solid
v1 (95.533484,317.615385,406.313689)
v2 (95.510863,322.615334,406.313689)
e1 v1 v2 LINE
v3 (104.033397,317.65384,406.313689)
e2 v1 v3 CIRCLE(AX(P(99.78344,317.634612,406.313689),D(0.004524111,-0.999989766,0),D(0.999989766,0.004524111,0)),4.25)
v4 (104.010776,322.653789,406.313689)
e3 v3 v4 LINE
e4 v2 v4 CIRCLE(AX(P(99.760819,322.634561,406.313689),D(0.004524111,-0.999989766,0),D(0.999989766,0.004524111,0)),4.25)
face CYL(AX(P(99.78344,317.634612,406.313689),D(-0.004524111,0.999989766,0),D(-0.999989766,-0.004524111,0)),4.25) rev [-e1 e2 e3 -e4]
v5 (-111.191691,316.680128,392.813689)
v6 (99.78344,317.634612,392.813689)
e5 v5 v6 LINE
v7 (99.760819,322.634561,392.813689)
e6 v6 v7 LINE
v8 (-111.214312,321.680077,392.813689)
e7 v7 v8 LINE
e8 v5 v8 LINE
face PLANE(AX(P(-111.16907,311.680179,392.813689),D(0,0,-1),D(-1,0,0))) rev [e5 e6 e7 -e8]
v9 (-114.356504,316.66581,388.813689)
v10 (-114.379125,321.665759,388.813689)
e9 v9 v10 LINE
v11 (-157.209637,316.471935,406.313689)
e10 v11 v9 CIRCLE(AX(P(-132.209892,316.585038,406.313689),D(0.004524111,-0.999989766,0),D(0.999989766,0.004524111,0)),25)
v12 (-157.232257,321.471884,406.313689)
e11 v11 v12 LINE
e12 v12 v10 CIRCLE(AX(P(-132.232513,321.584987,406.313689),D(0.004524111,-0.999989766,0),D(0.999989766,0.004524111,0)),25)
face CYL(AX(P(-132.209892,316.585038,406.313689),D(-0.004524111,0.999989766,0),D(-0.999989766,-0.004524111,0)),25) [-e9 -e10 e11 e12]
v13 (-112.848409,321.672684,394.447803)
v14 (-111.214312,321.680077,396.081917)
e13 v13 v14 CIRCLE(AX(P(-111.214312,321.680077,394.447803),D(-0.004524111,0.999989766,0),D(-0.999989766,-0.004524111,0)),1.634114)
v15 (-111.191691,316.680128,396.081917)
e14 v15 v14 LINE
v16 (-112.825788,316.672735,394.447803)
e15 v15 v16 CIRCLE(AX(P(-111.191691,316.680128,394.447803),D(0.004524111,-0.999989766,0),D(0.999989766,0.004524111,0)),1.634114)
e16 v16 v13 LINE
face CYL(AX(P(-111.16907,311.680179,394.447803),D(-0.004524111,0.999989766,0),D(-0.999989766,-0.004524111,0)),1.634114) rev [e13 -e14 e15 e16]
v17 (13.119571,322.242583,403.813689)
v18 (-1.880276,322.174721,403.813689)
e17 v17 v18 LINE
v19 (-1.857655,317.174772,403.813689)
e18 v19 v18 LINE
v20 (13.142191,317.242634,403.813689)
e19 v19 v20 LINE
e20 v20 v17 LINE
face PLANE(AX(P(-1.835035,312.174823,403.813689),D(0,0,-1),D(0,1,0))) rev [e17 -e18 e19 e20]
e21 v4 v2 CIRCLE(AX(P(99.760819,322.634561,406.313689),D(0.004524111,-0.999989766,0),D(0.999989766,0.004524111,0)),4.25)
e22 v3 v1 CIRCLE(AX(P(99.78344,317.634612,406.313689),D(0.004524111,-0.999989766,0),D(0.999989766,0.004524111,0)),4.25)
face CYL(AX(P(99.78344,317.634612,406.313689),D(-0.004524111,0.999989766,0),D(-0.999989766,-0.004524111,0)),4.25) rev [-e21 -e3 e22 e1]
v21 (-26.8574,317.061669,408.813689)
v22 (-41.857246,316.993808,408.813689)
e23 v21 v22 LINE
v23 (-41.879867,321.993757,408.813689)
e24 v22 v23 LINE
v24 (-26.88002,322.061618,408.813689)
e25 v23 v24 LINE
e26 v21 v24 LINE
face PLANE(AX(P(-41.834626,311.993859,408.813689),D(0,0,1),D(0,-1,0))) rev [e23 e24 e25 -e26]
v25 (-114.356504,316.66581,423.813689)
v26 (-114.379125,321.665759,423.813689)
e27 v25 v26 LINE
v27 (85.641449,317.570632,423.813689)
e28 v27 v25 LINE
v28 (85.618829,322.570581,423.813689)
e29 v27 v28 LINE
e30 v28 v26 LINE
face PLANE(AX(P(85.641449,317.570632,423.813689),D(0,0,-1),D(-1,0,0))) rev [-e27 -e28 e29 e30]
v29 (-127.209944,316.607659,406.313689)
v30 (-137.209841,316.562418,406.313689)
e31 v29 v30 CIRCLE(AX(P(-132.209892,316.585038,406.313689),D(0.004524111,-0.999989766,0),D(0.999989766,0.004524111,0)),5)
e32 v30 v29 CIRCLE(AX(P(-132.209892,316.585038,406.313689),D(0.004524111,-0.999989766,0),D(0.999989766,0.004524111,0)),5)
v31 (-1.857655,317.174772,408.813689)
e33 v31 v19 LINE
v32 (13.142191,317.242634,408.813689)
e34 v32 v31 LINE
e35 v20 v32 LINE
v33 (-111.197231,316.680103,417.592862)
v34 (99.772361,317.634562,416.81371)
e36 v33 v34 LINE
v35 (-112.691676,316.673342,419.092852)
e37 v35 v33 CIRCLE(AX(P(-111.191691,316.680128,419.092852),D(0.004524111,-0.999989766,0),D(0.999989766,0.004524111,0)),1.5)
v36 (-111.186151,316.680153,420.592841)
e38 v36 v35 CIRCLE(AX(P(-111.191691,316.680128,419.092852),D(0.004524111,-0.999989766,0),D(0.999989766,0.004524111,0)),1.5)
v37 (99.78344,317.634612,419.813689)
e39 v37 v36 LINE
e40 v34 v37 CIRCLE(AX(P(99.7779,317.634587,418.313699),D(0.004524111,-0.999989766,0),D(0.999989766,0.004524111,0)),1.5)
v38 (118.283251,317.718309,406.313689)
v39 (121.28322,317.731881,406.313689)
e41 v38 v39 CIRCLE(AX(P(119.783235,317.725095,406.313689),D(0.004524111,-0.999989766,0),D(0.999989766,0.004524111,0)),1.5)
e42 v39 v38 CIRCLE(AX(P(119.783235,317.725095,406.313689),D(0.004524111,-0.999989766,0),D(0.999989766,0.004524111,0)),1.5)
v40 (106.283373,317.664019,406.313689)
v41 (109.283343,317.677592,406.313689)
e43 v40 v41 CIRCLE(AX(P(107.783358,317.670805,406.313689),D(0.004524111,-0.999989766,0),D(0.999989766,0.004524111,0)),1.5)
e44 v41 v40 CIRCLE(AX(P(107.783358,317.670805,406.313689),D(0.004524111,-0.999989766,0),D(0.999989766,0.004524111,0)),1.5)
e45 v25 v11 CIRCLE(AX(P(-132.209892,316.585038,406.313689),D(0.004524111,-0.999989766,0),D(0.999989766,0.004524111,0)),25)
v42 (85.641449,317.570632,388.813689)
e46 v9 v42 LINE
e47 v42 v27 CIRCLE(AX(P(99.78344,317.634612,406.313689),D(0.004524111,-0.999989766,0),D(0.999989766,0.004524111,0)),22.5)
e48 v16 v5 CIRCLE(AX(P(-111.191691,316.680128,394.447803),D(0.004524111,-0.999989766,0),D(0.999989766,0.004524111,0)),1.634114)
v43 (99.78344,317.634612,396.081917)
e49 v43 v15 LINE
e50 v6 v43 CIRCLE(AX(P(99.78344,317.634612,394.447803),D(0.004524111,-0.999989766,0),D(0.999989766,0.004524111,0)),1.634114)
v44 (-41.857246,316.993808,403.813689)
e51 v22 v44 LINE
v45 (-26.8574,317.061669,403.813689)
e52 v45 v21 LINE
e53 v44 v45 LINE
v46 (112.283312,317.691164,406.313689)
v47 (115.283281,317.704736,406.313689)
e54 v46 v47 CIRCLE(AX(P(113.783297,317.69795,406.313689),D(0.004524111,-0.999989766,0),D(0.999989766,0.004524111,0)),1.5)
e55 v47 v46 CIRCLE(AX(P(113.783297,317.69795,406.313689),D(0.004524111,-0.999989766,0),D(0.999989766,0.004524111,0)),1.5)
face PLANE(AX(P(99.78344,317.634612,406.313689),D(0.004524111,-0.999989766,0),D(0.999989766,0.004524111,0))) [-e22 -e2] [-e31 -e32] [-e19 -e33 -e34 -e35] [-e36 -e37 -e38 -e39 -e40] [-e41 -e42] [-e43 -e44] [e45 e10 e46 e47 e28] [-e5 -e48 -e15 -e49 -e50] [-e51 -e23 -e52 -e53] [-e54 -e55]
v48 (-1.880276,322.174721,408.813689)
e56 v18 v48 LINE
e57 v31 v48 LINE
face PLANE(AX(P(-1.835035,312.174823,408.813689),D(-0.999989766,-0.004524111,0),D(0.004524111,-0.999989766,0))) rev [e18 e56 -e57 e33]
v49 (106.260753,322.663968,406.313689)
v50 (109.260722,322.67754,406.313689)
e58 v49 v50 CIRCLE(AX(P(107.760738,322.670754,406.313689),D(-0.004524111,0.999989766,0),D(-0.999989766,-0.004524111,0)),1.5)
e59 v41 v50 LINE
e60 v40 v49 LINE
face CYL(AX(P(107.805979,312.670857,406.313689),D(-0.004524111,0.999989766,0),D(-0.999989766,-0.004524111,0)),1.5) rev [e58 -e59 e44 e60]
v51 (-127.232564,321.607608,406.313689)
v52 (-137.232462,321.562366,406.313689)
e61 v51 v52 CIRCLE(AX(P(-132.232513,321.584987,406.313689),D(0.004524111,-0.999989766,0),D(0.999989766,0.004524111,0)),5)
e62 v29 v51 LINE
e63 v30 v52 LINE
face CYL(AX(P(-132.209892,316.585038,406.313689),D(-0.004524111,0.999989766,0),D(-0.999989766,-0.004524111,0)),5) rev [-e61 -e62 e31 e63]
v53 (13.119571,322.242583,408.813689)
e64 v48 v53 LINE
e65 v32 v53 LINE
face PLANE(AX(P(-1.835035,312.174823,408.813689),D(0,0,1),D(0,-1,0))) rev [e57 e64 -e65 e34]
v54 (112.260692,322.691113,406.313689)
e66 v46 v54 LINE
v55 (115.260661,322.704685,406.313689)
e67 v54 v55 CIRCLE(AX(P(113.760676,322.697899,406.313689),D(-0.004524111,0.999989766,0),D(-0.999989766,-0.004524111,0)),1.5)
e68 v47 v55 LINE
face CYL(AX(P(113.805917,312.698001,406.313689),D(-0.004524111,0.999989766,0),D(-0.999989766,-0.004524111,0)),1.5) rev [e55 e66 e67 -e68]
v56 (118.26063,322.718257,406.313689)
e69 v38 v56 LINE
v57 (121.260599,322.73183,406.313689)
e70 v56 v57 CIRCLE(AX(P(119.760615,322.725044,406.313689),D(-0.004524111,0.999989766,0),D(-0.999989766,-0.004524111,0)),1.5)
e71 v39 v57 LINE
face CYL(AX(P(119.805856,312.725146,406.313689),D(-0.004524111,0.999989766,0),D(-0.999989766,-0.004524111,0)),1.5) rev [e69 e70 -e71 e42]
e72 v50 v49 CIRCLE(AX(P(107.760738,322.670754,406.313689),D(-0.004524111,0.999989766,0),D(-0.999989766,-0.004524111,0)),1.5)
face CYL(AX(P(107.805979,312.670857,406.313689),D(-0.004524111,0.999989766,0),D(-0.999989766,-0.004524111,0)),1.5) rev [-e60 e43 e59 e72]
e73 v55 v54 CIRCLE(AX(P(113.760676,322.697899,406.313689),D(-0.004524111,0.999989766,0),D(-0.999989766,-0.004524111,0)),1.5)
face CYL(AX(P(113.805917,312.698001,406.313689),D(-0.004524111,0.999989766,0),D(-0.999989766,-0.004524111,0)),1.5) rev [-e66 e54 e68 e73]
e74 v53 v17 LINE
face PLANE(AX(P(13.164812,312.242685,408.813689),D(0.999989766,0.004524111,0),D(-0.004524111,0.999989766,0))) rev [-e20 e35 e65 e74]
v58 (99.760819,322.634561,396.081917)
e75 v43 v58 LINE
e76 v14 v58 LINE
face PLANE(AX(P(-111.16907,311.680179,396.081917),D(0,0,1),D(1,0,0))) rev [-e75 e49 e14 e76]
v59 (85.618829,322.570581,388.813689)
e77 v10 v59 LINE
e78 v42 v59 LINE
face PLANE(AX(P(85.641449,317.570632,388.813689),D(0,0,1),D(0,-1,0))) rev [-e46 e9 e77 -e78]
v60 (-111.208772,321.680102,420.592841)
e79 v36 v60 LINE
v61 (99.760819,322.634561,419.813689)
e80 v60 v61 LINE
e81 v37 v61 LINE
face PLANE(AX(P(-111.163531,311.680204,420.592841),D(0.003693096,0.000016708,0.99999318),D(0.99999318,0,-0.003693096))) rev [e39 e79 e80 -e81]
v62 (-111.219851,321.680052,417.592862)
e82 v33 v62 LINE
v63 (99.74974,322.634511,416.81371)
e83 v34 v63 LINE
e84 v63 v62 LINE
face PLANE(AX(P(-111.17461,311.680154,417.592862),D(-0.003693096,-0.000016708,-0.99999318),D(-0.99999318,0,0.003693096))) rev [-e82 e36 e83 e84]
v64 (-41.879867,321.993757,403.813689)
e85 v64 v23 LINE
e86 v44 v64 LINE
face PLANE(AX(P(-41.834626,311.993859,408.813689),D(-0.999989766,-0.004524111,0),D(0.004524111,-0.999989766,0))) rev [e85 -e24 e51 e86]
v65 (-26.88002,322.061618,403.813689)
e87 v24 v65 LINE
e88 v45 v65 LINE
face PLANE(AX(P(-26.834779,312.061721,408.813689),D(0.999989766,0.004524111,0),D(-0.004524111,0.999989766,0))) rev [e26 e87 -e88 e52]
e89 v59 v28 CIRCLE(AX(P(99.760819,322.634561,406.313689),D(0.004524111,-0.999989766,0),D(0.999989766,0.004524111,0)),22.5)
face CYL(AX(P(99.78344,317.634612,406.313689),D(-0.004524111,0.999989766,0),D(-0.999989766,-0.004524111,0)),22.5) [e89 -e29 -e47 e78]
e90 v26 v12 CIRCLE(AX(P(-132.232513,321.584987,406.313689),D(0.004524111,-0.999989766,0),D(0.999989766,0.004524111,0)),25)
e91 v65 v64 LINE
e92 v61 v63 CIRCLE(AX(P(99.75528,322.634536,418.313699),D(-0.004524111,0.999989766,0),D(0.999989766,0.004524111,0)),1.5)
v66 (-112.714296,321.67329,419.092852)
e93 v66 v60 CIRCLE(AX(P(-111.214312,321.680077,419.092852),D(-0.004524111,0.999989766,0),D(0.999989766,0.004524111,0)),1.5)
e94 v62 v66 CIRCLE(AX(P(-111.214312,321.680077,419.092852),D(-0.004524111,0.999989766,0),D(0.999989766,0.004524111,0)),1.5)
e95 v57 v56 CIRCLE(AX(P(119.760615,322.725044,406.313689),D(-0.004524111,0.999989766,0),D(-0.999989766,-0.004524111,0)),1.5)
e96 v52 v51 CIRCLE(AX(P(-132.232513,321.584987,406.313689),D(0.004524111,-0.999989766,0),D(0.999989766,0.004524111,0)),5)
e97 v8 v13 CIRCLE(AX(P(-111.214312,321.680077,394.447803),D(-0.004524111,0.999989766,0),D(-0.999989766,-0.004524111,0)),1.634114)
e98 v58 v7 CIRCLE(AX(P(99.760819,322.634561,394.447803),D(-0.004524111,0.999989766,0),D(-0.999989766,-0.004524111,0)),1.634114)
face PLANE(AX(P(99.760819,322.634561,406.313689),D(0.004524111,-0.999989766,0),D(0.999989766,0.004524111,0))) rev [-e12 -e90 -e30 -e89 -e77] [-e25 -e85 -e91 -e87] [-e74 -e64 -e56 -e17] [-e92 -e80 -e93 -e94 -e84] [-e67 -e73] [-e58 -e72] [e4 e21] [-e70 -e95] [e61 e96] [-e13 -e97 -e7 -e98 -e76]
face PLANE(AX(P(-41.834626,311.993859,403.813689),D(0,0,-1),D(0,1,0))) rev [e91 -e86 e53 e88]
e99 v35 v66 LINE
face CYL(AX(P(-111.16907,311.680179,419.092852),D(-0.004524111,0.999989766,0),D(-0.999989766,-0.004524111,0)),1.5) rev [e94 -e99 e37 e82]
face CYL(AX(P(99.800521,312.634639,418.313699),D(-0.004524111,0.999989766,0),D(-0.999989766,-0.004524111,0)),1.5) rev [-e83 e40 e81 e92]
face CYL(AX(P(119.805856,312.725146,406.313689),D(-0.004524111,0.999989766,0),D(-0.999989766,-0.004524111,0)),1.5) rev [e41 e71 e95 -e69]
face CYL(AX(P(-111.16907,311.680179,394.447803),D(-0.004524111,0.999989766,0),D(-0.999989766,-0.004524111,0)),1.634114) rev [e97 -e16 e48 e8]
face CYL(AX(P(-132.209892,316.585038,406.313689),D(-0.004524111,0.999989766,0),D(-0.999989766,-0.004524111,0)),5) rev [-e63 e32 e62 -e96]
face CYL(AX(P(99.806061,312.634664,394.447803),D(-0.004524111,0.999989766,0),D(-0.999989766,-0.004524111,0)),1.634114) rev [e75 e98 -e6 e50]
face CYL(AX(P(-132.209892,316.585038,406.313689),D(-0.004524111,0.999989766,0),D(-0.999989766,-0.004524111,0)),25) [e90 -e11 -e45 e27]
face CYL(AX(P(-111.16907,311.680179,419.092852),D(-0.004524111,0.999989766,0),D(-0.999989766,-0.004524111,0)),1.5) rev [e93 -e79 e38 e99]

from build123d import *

# Parameters (mm, degrees)
SKETCH_1_R          = 4.25
SKETCH_1_R_2        = 5
EXTRUDE_1_DEPTH     = 5
SKETCH_2_R          = 4.25
SKETCH_2_R_2        = 1.5
CUT_EXTRUDE_1_DEPTH = 10
CUT_EXTRUDE_2_DEPTH = 10
SKETCH_4_W          = 15
SKETCH_4_H          = 5
CUT_EXTRUDE_3_DEPTH = 10


with BuildPart() as part:
    # 草图1 → 凸台-拉伸1 (new body)
    with BuildSketch(Plane(origin=(-1.457577728, 322.176633369, 0), x_dir=(0.9999897661580252, 0.004524110875991417, 0), z_dir=(0.004524110875991416, -0.999989766158025, 0))):
        with BuildLine():
            Line((87.077297431, 423.813689202), (-112.922702569, 423.813689202))
            ThreePointArc((-112.922702569, 423.813689202), (-155.776273641, 406.313689202), (-112.922702569, 388.813689202))
            Line((-112.922702569, 388.813689202), (87.077297431, 388.813689202))
            ThreePointArc((87.077297431, 388.813689202), (123.719433055, 406.313689202), (87.077297431, 423.813689202))
        make_face()
        with Locations((101.219433055, 406.313689202)):
            Circle(SKETCH_1_R, mode=Mode.SUBTRACT)
        with Locations((-130.776273641, 406.313689202)):
            Circle(SKETCH_1_R_2, mode=Mode.SUBTRACT)
    extrude(amount=EXTRUDE_1_DEPTH)

    # 草图2 → 切除-拉伸1 (cut)
    with BuildSketch(Plane(origin=(-1.457577728, 322.176633369, 0), x_dir=(0.9999897661580252, 0.004524110875991416, 0), z_dir=(-0.004524110875991415, 0.999989766158025, 0))):
        with Locations((101.219433055, -406.313689202)):
            Circle(SKETCH_2_R)
        with Locations(Location((121.219433055, -406.313689202, 0), (0, 0, 180))):
            Circle(SKETCH_2_R_2)
        with Locations(Location((115.219433055, -406.313689202, 0), (0, 0, 180))):
            Circle(SKETCH_2_R_2)
        with Locations(Location((109.219433055, -406.313689202, 0), (0, 0, 180))):
            Circle(SKETCH_2_R_2)
        with Locations((-41.214218621, -347.791207337)):
            Circle(SKETCH_2_R_2)
        with Locations((-45.456859308, -343.54856665)):
            Circle(SKETCH_2_R_2)
        with Locations((-49.699499995, -339.305925963)):
            Circle(SKETCH_2_R_2)
        with Locations((-114.690511434, -191.551626966)):
            Circle(SKETCH_2_R_2)
        with Locations((-114.690511434, -185.551626966)):
            Circle(SKETCH_2_R_2)
        with Locations((-114.690511434, -179.551626966)):
            Circle(SKETCH_2_R_2)
        with Locations((-56.168029569, -29.117975291)):
            Circle(SKETCH_2_R_2)
        with Locations((-51.925388882, -24.875334604)):
            Circle(SKETCH_2_R_2)
        with Locations((-47.682748195, -20.632693917)):
            Circle(SKETCH_2_R_2)
        with Locations((100.071550802, 44.358317523)):
            Circle(SKETCH_2_R_2)
        with Locations((106.071550802, 44.358317523)):
            Circle(SKETCH_2_R_2)
        with Locations((112.071550802, 44.358317523)):
            Circle(SKETCH_2_R_2)
        with Locations((262.505202477, -14.164164342)):
            Circle(SKETCH_2_R_2)
        with Locations((266.747843164, -18.406805029)):
            Circle(SKETCH_2_R_2)
        with Locations((270.990483851, -22.649445716)):
            Circle(SKETCH_2_R_2)
        with Locations((335.981495291, -170.403744713)):
            Circle(SKETCH_2_R_2)
        with Locations((335.981495291, -176.403744713)):
            Circle(SKETCH_2_R_2)
        with Locations((335.981495291, -182.403744713)):
            Circle(SKETCH_2_R_2)
        with Locations((277.459013426, -332.837396388)):
            Circle(SKETCH_2_R_2)
        with Locations((273.216372738, -337.080037075)):
            Circle(SKETCH_2_R_2)
        with Locations((268.973732051, -341.322677763)):
            Circle(SKETCH_2_R_2)
    extrude(amount=-CUT_EXTRUDE_1_DEPTH, mode=Mode.SUBTRACT)

    # 草图3 → 切除-拉伸2 (cut)
    with BuildSketch(Plane(origin=(-1.457577728, 322.176633369, 0), x_dir=(0.9999897661580252, 0.004524110875991416, 0), z_dir=(-0.004524110875991415, 0.999989766158025, 0))):
        with BuildLine():
            Line((-109.757857106, -392.813689202), (101.219433055, -392.813689202))
            ThreePointArc((101.219433055, -392.813689202), (102.853546755, -394.447802903), (101.219433055, -396.081916603))
            Line((101.219433055, -396.081916603), (-109.757857106, -396.081916603))
            ThreePointArc((-109.757857106, -396.081916603), (-111.391970807, -394.447802903), (-109.757857106, -392.813689202))
        make_face()
        with BuildLine():
            Line((-109.752317405, -420.592841481), (101.219433055, -419.813689202))
            ThreePointArc((101.219433055, -419.813689202), (102.713883124, -418.30815973), (101.208353652, -416.813709661))
            Line((101.208353652, -416.813709661), (-109.763396807, -417.59286194))
            ThreePointArc((-109.763396807, -417.59286194), (-111.257846876, -419.098391411), (-109.752317405, -420.592841481))
        make_face()
    extrude(amount=-CUT_EXTRUDE_2_DEPTH, mode=Mode.SUBTRACT)

    # 草图4 → 切除-拉伸3 (cut)
    with BuildSketch(Plane(origin=(-1.457577728, 322.176633369, 0), x_dir=(0.9999897661580252, 0.004524110875991416, 0), z_dir=(-0.004524110875991415, 0.999989766158025, 0))):
        with Locations((-32.922702569, -406.313689202)):
            Rectangle(SKETCH_4_W, SKETCH_4_H)
        with Locations((7.077297431, -406.313689202)):
            Rectangle(SKETCH_4_W, SKETCH_4_H)
    extrude(amount=-CUT_EXTRUDE_3_DEPTH, mode=Mode.SUBTRACT)


solid = part.part
